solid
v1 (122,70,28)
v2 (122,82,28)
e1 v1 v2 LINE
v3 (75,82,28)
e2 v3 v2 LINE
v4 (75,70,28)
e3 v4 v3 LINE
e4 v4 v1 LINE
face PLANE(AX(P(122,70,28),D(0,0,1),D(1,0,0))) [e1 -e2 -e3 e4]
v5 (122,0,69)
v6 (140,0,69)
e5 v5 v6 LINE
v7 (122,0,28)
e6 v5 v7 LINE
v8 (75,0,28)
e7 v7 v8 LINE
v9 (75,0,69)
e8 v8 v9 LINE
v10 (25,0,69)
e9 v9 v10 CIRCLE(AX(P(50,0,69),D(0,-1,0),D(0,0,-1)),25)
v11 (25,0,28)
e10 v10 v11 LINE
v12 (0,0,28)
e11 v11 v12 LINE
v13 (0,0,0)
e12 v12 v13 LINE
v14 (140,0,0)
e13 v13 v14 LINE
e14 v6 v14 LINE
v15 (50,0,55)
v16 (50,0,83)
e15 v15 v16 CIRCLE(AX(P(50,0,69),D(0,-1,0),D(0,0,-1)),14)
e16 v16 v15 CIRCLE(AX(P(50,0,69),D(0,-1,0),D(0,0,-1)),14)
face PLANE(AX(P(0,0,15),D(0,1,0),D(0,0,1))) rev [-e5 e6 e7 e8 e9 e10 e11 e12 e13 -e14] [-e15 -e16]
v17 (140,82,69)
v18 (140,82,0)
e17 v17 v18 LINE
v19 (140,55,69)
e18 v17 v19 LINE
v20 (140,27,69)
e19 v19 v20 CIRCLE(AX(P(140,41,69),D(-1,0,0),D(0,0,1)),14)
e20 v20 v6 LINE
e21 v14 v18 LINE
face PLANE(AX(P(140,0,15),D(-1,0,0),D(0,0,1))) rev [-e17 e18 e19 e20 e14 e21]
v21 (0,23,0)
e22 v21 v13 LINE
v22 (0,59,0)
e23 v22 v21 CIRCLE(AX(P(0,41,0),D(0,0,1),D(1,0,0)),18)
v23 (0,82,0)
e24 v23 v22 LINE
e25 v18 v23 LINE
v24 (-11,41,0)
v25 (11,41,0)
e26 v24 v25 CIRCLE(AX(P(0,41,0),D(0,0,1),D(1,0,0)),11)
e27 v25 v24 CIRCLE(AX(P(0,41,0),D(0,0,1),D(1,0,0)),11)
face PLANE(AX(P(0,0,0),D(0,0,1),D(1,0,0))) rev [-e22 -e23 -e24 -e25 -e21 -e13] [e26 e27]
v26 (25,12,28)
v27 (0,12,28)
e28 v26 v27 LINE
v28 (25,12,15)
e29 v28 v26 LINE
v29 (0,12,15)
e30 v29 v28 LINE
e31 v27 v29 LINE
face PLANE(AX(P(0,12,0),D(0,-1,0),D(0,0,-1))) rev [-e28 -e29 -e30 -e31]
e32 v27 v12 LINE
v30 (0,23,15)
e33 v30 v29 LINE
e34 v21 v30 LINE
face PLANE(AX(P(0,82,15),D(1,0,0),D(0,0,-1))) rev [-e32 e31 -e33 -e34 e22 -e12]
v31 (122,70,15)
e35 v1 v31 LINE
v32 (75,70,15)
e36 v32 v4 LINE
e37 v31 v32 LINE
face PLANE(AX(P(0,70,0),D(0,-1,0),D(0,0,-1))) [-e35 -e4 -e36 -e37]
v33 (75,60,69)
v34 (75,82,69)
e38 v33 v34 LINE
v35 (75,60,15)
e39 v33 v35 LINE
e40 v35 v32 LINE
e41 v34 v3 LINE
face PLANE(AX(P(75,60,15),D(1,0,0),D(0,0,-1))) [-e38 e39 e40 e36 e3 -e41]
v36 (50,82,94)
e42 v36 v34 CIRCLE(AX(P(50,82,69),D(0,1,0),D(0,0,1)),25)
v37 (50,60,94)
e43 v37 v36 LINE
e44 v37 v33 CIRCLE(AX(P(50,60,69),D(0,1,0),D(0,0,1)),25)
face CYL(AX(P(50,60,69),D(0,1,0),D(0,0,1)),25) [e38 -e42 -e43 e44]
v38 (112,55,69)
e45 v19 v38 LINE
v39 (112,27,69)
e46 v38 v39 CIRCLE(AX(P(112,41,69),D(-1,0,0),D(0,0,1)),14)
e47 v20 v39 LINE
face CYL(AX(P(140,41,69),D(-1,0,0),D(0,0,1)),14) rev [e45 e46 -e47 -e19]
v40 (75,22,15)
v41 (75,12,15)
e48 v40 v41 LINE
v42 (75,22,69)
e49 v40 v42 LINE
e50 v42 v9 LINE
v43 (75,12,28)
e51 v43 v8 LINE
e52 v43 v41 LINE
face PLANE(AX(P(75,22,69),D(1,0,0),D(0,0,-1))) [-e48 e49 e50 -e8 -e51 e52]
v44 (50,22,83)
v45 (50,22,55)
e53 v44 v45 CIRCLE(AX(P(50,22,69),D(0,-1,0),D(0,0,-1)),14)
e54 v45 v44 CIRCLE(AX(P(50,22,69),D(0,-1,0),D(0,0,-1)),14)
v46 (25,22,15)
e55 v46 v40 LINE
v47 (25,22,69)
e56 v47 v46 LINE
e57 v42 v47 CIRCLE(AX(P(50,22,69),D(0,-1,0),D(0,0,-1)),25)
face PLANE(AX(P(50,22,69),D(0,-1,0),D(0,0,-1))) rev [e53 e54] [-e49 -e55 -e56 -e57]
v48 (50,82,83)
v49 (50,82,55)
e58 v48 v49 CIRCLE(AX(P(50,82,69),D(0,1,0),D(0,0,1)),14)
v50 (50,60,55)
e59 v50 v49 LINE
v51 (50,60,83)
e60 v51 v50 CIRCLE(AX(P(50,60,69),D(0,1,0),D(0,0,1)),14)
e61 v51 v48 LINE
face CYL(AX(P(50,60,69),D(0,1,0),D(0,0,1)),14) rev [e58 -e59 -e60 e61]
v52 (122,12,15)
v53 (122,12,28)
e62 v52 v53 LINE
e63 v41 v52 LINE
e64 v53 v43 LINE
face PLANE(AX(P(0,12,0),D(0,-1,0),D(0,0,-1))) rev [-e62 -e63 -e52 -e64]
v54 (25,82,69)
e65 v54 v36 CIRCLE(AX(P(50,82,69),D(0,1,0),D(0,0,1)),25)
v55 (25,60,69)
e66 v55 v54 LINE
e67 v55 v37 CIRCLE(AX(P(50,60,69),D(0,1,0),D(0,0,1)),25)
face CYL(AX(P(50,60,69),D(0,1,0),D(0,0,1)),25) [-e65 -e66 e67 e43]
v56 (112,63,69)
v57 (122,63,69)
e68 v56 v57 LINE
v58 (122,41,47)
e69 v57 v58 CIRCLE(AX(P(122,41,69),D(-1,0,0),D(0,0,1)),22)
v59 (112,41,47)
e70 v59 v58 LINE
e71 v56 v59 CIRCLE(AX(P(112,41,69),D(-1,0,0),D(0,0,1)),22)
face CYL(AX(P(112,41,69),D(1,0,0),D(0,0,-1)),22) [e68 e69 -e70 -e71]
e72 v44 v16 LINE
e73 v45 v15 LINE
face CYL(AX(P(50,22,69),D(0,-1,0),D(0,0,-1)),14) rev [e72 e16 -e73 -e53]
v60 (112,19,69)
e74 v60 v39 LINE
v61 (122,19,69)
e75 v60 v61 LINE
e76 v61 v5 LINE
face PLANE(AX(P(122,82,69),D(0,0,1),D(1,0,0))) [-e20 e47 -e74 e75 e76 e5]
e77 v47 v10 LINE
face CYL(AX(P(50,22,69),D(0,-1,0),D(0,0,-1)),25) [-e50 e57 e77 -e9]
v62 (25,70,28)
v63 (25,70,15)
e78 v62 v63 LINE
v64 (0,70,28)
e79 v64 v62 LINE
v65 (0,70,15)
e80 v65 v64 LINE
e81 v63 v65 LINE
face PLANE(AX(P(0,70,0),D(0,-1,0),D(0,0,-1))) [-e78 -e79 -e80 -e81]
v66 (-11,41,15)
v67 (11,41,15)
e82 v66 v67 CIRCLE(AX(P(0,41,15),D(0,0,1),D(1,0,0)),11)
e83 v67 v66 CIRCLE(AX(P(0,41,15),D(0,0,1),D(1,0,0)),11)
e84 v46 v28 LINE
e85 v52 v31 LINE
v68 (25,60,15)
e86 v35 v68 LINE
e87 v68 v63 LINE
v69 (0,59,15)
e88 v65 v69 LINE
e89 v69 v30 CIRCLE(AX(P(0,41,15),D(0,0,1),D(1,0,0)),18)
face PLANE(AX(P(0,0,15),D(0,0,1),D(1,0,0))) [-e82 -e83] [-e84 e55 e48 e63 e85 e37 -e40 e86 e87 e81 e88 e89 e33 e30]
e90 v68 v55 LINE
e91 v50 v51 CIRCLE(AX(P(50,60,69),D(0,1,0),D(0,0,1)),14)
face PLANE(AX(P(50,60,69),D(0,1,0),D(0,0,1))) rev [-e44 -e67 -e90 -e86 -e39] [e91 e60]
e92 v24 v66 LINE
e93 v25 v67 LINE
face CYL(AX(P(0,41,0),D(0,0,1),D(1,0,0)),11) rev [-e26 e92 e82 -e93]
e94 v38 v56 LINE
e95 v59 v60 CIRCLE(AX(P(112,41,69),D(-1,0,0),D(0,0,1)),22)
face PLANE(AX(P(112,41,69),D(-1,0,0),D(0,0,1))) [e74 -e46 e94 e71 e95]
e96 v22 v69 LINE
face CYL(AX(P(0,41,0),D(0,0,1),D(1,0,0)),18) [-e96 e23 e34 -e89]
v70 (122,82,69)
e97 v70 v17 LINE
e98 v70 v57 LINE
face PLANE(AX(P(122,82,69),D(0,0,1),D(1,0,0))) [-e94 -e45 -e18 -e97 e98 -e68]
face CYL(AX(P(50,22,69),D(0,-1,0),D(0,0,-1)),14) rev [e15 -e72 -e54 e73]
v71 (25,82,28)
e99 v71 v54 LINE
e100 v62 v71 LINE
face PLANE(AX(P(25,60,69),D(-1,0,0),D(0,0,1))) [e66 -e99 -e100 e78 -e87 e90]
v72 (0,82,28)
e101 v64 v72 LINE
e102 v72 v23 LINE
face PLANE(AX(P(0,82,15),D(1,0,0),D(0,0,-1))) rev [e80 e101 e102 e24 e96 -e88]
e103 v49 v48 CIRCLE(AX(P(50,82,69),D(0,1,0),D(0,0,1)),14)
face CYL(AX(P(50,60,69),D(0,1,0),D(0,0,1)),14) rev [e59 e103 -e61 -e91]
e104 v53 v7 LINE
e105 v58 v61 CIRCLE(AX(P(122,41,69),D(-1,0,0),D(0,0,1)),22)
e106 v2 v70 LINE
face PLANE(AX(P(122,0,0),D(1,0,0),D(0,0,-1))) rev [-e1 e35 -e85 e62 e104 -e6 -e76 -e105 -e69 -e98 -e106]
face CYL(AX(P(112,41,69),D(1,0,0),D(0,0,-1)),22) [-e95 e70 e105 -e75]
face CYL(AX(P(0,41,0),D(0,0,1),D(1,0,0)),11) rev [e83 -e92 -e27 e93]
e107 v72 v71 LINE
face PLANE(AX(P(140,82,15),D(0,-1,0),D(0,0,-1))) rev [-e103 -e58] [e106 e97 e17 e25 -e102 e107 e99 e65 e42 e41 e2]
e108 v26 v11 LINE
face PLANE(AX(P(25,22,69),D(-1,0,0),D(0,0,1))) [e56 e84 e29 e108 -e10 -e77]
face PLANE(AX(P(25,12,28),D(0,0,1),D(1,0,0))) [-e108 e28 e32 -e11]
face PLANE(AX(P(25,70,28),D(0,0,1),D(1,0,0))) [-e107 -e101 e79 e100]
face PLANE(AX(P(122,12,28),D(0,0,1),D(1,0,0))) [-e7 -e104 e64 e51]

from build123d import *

# Parameters (mm, degrees)
BASE_PLATE_SKETCH_W         = 140
BASE_PLATE_SKETCH_H         = 82
BASE_PLATE_DEPTH            = 15
BACK_WALL_SKETCH_W          = 54
BACK_WALL_SKETCH_H          = 82
BACK_WALL_DEPTH             = 18
REAR_HALF_BOSS_DEPTH        = 10
REAR_HALF_ROUND_CUT_DEPTH   = 28
LOWER_LUG_DEPTH             = 22
SPACER_BLOCK_1_SKETCH_W     = 47
SPACER_BLOCK_1_SKETCH_H     = 13
SPACER_BLOCK_1_DEPTH        = 12
SPACER_BLOCK_2_SKETCH_W     = 25
SPACER_BLOCK_2_SKETCH_H     = 13
SPACER_BLOCK_2_DEPTH        = 12
SPACER_BLOCK_3_SKETCH_W     = 47
SPACER_BLOCK_3_SKETCH_H     = 13
SPACER_BLOCK_3_DEPTH        = 12
UPPER_START                 = -22
UPPER_LUG_DEPTH             = 22
SPACER_BLOCK_4_SKETCH_W     = 25
SPACER_BLOCK_4_SKETCH_H     = 13
SPACER_BLOCK_4_DEPTH        = 12
SIDE_HALF_BOSS_DEPTH        = 15
SIDE_BORE_SKETCH_R          = 11
SIDE_BORE_22_DEPTH          = 15
UPPER_PIN_HOLE_SKETCH_R     = 14
UPPER_LUG_PIN_HOLE_28_DEPTH = 22
LOWER_START                 = -22
LOWER_PIN_HOLE_SKETCH_R     = 14
LOWER_LUG_PIN_HOLE_28_DEPTH = 22


with BuildPart() as part:
    # Base Plate Sketch → Base Plate (new body)
    with BuildSketch(Plane.XY):
        with Locations((70, 41)):
            Rectangle(BASE_PLATE_SKETCH_W, BASE_PLATE_SKETCH_H)
    extrude(amount=BASE_PLATE_DEPTH)

    # Back Wall Sketch → Back Wall (add)
    with BuildSketch(Plane(origin=(140, 0, 0), x_dir=(0, 0, -1), z_dir=(1, 0, 0))):
        with Locations((-42, 41)):
            Rectangle(BACK_WALL_SKETCH_W, BACK_WALL_SKETCH_H)
    extrude(amount=-BACK_WALL_DEPTH)

    # Rear Half Boss Sketch → Rear Half Boss (add)
    with BuildSketch(Plane.ZY.offset(-122)):
        with BuildLine():
            Line((69, 63), (69, 19))
            ThreePointArc((69, 19), (47, 41), (69, 63))
        make_face()
    extrude(amount=REAR_HALF_BOSS_DEPTH)

    # Rear Half-Round Cut Sketch → Rear Half-Round Cut (cut)
    with BuildSketch(Plane.ZY.offset(-112)):
        with BuildLine():
            Line((69, 55), (69, 27))
            ThreePointArc((69, 27), (55, 41), (69, 55))
        make_face()
    extrude(amount=-REAR_HALF_ROUND_CUT_DEPTH, mode=Mode.SUBTRACT)

    # Lower Lug Sketch → Lower Lug (add)
    with BuildSketch(Plane.XZ):
        with BuildLine():
            Line((75, 69), (75, 15))
            Line((75, 15), (25, 15))
            Line((25, 15), (25, 69))
            ThreePointArc((25, 69), (50, 94), (75, 69))
        make_face()
    extrude(amount=-LOWER_LUG_DEPTH)

    # Spacer Block 1 Sketch → Spacer Block 1 (add)
    with BuildSketch(Plane.XZ):
        with Locations((98.5, 21.5)):
            Rectangle(SPACER_BLOCK_1_SKETCH_W, SPACER_BLOCK_1_SKETCH_H)
    extrude(amount=-SPACER_BLOCK_1_DEPTH)

    # Spacer Block 2 Sketch → Spacer Block 2 (add)
    with BuildSketch(Plane.XZ):
        with Locations((12.5, 21.5)):
            Rectangle(SPACER_BLOCK_2_SKETCH_W, SPACER_BLOCK_2_SKETCH_H)
    extrude(amount=-SPACER_BLOCK_2_DEPTH)

    # Spacer Block 3 Sketch → Spacer Block 3 (add)
    with BuildSketch(Plane(origin=(0, 82, 0), x_dir=(1, 0, 0), z_dir=(0, 1, 0))):
        with Locations((98.5, -21.5)):
            Rectangle(SPACER_BLOCK_3_SKETCH_W, SPACER_BLOCK_3_SKETCH_H)
    extrude(amount=-SPACER_BLOCK_3_DEPTH)

    # Upper Lug Sketch → Upper Lug (add)
    with BuildSketch(Plane(origin=(0, 82, 0), x_dir=(1, 0, 0), z_dir=(0, 1, 0)).offset(UPPER_START)):
        with BuildLine():
            Line((25, -15), (75, -15))
            Line((75, -15), (75, -69))
            ThreePointArc((75, -69), (50, -94), (25, -69))
            Line((25, -69), (25, -15))
        make_face()
    extrude(amount=UPPER_LUG_DEPTH)

    # Spacer Block 4 Sketch → Spacer Block 4 (add)
    with BuildSketch(Plane(origin=(0, 82, 0), x_dir=(1, 0, 0), z_dir=(0, 1, 0))):
        with Locations((12.5, -21.5)):
            Rectangle(SPACER_BLOCK_4_SKETCH_W, SPACER_BLOCK_4_SKETCH_H)
    extrude(amount=-SPACER_BLOCK_4_DEPTH)

    # Side Half Boss Sketch → Side Half Boss (add)
    with BuildSketch(Plane.XY.offset(15)):
        with BuildLine():
            Line((0, 59), (0, 23))
            ThreePointArc((0, 23), (-18, 41), (0, 59))
        make_face()
    extrude(amount=-SIDE_HALF_BOSS_DEPTH)

    # Side Bore Sketch → Side Bore Ø22 (cut)
    with BuildSketch(Plane.XY.offset(15)):
        with Locations((0, 41)):
            Circle(SIDE_BORE_SKETCH_R)
    extrude(amount=-SIDE_BORE_22_DEPTH, mode=Mode.SUBTRACT)

    # Upper Pin Hole Sketch → Upper Lug Pin Hole Ø28 (cut)
    with BuildSketch(Plane(origin=(0, 82, 0), x_dir=(1, 0, 0), z_dir=(0, 1, 0))):
        with Locations(Location((50, -69, 0), (0, 0, 270))):
            Circle(UPPER_PIN_HOLE_SKETCH_R)
    extrude(amount=-UPPER_LUG_PIN_HOLE_28_DEPTH, mode=Mode.SUBTRACT)

    # Lower Pin Hole Sketch → Lower Lug Pin Hole Ø28 (cut)
    with BuildSketch(Plane.XZ.offset(LOWER_START)):
        with Locations(Location((50, 69, 0), (0, 0, 90))):
            Circle(LOWER_PIN_HOLE_SKETCH_R)
    extrude(amount=LOWER_LUG_PIN_HOLE_28_DEPTH, mode=Mode.SUBTRACT)


solid = part.part
